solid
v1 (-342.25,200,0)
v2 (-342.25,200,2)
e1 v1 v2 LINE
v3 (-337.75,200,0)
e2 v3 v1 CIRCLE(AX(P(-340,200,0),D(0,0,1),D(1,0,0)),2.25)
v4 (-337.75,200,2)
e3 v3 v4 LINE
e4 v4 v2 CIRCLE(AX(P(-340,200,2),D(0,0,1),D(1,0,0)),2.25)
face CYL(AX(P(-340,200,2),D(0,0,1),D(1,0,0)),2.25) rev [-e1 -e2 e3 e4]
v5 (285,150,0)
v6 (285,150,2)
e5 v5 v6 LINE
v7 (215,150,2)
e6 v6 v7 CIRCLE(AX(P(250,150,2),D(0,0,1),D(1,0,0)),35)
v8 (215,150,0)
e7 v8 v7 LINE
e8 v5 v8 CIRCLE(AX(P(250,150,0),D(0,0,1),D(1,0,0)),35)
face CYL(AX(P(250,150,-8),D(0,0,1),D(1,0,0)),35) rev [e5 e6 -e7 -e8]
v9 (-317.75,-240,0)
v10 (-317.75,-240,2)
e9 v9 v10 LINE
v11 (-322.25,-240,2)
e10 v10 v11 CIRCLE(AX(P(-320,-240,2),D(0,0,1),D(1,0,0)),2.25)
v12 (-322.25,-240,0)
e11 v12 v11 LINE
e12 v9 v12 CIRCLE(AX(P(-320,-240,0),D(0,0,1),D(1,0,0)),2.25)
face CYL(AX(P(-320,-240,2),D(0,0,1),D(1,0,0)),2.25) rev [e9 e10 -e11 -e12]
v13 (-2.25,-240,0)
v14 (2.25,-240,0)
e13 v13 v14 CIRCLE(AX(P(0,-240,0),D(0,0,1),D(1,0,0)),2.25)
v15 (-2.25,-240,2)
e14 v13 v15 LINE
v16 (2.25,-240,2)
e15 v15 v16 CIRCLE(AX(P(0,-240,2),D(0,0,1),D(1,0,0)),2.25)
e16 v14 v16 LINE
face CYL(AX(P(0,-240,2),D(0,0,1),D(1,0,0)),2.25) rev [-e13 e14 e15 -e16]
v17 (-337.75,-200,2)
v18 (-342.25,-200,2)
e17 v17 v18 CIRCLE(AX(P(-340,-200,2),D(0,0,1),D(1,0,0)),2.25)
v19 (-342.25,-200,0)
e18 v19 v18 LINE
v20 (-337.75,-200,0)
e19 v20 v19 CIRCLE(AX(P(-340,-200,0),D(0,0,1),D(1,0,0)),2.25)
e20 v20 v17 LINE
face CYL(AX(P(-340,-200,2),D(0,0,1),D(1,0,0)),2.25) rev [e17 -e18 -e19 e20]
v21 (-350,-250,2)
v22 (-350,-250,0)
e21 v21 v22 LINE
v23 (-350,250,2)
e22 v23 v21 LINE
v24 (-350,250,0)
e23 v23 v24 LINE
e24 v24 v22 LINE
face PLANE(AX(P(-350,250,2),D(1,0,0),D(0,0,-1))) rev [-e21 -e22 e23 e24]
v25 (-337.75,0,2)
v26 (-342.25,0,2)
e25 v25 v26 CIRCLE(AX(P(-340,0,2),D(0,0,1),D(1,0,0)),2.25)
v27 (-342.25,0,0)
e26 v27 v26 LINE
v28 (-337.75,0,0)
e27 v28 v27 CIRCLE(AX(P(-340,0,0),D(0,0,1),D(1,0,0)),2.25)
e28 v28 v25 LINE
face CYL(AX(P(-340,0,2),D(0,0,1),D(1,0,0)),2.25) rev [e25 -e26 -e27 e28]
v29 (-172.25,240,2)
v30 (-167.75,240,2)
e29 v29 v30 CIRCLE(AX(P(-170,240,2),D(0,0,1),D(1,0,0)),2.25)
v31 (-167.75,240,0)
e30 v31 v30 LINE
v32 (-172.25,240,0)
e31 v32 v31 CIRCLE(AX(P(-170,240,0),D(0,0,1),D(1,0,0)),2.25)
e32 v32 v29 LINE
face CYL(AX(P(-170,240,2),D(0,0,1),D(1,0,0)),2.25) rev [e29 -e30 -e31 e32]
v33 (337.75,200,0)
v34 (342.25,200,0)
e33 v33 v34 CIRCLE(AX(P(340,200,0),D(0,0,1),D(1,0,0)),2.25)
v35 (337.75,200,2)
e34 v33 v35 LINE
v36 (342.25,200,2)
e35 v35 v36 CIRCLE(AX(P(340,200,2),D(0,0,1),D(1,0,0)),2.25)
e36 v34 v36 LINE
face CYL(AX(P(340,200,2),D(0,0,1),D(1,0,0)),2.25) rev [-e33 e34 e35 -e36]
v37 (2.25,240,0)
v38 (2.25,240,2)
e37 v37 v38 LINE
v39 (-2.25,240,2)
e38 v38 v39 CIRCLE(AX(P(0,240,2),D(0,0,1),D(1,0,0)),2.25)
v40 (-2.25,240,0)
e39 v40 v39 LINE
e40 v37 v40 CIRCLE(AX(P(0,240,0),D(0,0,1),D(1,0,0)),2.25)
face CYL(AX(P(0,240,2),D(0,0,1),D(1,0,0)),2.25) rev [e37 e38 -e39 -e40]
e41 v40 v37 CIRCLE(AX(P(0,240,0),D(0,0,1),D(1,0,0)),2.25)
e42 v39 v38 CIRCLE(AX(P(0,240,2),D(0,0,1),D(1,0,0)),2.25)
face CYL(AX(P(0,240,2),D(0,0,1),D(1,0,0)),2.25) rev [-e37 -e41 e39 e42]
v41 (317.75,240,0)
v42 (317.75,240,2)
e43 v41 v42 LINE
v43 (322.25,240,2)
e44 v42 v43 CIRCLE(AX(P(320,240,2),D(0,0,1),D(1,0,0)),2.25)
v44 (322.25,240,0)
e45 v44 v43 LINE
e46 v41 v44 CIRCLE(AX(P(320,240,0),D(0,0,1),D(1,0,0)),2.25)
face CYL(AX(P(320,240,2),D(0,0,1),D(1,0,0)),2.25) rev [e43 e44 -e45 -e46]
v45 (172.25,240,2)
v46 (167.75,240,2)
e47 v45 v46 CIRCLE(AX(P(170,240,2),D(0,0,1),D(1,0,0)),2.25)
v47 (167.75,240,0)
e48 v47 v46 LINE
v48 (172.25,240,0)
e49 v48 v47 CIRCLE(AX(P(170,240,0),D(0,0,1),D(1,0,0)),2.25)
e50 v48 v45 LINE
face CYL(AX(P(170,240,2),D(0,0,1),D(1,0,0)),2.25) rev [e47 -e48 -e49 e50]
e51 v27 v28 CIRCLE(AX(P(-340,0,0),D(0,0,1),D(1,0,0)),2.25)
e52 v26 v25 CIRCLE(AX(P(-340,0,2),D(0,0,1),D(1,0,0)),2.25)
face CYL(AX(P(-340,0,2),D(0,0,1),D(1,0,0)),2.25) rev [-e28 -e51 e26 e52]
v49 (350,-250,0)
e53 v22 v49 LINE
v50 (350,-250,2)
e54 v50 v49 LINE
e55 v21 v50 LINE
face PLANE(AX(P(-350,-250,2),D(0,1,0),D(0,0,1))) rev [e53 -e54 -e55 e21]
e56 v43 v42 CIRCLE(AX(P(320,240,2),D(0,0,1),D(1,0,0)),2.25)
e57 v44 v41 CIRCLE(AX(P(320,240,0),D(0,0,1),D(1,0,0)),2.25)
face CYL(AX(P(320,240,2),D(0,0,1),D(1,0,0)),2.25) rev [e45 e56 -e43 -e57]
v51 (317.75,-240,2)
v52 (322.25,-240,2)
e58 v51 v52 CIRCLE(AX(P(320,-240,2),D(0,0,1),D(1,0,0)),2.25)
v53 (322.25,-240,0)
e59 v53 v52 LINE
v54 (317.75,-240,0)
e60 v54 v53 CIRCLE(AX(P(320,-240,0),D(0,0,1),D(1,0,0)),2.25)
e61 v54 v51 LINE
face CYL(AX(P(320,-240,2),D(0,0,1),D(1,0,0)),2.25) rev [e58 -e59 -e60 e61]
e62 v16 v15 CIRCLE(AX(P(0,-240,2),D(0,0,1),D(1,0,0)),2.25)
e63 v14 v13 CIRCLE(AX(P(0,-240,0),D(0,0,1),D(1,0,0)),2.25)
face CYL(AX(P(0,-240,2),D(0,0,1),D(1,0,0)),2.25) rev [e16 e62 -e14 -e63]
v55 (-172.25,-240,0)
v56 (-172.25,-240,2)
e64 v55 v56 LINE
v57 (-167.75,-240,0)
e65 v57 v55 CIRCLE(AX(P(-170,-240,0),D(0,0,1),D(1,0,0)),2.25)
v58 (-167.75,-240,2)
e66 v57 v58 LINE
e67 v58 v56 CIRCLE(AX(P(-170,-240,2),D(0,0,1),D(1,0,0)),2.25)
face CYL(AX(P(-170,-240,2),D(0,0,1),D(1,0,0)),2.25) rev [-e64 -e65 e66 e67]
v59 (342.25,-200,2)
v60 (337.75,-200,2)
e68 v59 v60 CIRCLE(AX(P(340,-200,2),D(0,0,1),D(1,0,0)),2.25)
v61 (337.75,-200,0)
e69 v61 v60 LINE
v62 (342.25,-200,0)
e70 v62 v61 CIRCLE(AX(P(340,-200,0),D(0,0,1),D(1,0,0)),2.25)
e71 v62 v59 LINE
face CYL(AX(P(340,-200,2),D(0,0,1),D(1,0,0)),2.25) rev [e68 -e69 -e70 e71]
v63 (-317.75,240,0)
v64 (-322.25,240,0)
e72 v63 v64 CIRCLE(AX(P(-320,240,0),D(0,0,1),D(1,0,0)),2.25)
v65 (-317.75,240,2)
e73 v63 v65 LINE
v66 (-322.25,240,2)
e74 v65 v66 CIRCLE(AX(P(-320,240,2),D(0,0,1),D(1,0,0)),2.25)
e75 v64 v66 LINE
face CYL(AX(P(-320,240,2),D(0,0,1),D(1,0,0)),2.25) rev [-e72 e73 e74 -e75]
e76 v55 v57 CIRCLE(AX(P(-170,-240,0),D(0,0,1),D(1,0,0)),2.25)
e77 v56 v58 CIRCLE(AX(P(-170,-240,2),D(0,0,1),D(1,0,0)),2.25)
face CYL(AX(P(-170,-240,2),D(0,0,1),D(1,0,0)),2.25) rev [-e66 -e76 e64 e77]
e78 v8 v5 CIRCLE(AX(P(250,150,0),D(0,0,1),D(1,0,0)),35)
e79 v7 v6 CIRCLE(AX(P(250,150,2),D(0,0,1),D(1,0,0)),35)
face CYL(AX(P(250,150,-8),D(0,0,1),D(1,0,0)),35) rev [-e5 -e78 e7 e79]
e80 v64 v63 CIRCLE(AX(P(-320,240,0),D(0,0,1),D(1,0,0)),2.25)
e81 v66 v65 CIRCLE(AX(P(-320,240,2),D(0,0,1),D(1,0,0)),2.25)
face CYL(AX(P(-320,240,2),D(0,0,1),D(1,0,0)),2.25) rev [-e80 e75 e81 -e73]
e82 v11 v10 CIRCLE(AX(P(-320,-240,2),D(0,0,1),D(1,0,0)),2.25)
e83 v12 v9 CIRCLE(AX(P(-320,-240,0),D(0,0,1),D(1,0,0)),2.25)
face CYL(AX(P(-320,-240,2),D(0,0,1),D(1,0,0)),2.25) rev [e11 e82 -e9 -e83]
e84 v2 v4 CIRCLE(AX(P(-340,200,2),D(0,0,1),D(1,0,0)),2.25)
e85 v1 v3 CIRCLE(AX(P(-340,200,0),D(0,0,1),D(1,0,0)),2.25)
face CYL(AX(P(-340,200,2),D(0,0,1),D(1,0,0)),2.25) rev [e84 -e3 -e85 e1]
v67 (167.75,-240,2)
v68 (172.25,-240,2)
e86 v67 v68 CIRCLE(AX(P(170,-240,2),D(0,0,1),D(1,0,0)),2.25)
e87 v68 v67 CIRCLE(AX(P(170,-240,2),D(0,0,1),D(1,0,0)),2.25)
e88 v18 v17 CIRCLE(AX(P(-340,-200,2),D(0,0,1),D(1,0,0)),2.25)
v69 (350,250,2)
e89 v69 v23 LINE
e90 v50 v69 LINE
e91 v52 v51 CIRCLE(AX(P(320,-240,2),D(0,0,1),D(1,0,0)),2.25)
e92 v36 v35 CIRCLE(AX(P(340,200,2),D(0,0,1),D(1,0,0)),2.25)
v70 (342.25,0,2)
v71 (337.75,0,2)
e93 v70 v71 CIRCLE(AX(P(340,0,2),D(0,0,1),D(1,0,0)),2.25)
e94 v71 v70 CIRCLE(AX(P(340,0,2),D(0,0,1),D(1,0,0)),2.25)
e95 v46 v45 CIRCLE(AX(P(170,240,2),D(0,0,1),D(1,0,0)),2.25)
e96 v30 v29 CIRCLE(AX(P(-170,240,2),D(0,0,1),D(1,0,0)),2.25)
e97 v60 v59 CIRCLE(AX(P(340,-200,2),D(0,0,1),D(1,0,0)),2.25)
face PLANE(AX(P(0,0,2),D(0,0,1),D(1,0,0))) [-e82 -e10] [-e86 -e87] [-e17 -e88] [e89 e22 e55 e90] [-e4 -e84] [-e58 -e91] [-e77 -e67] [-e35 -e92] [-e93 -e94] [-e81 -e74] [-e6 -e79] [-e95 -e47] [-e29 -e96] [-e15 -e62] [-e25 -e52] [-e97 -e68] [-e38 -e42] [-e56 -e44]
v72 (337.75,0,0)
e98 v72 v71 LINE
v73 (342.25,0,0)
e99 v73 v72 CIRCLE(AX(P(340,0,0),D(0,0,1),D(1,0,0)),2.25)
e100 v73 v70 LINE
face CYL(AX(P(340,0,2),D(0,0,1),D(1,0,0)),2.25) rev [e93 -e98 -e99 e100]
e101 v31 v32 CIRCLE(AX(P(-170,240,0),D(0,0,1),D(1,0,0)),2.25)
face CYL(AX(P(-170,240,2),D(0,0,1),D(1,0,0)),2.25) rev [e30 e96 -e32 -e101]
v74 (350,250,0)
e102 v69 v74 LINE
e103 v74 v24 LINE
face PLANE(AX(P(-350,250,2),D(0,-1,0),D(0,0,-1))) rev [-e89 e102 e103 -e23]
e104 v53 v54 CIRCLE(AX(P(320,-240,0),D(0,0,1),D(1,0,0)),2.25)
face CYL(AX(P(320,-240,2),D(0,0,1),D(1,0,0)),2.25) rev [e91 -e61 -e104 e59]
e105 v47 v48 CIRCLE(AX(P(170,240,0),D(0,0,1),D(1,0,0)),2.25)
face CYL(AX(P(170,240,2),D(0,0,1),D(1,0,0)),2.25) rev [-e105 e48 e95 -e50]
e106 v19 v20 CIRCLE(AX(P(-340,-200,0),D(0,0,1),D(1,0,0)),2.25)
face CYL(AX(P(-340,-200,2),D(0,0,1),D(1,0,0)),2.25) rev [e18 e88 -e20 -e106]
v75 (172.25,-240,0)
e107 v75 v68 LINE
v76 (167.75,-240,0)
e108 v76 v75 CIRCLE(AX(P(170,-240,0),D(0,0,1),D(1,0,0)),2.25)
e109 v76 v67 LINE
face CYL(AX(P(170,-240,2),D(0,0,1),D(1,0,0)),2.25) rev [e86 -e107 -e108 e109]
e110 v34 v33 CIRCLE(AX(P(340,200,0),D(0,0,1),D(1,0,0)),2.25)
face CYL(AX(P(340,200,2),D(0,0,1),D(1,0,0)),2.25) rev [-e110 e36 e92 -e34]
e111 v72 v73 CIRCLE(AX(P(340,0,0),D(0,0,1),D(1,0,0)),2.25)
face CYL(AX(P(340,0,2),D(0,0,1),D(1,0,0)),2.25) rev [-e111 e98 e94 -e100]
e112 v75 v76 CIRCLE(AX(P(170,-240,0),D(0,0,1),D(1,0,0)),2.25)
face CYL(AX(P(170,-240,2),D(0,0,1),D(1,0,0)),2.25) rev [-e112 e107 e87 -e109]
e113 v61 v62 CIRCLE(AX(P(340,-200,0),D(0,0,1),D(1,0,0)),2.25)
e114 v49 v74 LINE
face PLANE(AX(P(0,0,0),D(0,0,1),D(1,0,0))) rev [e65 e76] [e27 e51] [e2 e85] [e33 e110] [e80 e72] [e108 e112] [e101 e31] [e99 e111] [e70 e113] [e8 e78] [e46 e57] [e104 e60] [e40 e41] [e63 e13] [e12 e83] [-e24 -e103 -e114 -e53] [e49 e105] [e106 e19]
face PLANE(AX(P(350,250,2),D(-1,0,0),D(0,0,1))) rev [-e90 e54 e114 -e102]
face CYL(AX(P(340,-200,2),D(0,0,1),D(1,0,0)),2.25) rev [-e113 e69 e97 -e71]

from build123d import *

# Parameters (mm, degrees)
SKETCH_1_W              = 700
SKETCH_1_H              = 500
EXTRUDE_1_DEPTH         = 2
HOLE_WIZARD_4_5_4_5_1_D = 4.5
SKETCH_4_R              = 35
CUT_EXTRUDE_1_DEPTH     = 10


with BuildPart() as part:
    # 草图1 → 凸台-拉伸1 (new body)
    with BuildSketch(Plane.XY):
        Rectangle(SKETCH_1_W, SKETCH_1_H)
    extrude(amount=EXTRUDE_1_DEPTH)

    # Ø4.5 (4.5) 直径孔1 (through all)
    with Locations(Plane.XY.offset(2)):
        with Locations((320, -240), (-340, 0), (0, -240), (340, 0), (0, 240), (-170, 240), (170, 240), (-170, -240), (170, -240), (-320, 240), (320, 240), (-340, 200), (-340, -200), (340, -200), (340, 200), (-320, -240)):
            Hole(HOLE_WIZARD_4_5_4_5_1_D / 2)

    # 草图4 → 切除-拉伸1 (cut)
    with BuildSketch(Plane.XY.offset(2)):
        with Locations((250, 150)):
            Circle(SKETCH_4_R)
    extrude(amount=-CUT_EXTRUDE_1_DEPTH, mode=Mode.SUBTRACT)


solid = part.part
